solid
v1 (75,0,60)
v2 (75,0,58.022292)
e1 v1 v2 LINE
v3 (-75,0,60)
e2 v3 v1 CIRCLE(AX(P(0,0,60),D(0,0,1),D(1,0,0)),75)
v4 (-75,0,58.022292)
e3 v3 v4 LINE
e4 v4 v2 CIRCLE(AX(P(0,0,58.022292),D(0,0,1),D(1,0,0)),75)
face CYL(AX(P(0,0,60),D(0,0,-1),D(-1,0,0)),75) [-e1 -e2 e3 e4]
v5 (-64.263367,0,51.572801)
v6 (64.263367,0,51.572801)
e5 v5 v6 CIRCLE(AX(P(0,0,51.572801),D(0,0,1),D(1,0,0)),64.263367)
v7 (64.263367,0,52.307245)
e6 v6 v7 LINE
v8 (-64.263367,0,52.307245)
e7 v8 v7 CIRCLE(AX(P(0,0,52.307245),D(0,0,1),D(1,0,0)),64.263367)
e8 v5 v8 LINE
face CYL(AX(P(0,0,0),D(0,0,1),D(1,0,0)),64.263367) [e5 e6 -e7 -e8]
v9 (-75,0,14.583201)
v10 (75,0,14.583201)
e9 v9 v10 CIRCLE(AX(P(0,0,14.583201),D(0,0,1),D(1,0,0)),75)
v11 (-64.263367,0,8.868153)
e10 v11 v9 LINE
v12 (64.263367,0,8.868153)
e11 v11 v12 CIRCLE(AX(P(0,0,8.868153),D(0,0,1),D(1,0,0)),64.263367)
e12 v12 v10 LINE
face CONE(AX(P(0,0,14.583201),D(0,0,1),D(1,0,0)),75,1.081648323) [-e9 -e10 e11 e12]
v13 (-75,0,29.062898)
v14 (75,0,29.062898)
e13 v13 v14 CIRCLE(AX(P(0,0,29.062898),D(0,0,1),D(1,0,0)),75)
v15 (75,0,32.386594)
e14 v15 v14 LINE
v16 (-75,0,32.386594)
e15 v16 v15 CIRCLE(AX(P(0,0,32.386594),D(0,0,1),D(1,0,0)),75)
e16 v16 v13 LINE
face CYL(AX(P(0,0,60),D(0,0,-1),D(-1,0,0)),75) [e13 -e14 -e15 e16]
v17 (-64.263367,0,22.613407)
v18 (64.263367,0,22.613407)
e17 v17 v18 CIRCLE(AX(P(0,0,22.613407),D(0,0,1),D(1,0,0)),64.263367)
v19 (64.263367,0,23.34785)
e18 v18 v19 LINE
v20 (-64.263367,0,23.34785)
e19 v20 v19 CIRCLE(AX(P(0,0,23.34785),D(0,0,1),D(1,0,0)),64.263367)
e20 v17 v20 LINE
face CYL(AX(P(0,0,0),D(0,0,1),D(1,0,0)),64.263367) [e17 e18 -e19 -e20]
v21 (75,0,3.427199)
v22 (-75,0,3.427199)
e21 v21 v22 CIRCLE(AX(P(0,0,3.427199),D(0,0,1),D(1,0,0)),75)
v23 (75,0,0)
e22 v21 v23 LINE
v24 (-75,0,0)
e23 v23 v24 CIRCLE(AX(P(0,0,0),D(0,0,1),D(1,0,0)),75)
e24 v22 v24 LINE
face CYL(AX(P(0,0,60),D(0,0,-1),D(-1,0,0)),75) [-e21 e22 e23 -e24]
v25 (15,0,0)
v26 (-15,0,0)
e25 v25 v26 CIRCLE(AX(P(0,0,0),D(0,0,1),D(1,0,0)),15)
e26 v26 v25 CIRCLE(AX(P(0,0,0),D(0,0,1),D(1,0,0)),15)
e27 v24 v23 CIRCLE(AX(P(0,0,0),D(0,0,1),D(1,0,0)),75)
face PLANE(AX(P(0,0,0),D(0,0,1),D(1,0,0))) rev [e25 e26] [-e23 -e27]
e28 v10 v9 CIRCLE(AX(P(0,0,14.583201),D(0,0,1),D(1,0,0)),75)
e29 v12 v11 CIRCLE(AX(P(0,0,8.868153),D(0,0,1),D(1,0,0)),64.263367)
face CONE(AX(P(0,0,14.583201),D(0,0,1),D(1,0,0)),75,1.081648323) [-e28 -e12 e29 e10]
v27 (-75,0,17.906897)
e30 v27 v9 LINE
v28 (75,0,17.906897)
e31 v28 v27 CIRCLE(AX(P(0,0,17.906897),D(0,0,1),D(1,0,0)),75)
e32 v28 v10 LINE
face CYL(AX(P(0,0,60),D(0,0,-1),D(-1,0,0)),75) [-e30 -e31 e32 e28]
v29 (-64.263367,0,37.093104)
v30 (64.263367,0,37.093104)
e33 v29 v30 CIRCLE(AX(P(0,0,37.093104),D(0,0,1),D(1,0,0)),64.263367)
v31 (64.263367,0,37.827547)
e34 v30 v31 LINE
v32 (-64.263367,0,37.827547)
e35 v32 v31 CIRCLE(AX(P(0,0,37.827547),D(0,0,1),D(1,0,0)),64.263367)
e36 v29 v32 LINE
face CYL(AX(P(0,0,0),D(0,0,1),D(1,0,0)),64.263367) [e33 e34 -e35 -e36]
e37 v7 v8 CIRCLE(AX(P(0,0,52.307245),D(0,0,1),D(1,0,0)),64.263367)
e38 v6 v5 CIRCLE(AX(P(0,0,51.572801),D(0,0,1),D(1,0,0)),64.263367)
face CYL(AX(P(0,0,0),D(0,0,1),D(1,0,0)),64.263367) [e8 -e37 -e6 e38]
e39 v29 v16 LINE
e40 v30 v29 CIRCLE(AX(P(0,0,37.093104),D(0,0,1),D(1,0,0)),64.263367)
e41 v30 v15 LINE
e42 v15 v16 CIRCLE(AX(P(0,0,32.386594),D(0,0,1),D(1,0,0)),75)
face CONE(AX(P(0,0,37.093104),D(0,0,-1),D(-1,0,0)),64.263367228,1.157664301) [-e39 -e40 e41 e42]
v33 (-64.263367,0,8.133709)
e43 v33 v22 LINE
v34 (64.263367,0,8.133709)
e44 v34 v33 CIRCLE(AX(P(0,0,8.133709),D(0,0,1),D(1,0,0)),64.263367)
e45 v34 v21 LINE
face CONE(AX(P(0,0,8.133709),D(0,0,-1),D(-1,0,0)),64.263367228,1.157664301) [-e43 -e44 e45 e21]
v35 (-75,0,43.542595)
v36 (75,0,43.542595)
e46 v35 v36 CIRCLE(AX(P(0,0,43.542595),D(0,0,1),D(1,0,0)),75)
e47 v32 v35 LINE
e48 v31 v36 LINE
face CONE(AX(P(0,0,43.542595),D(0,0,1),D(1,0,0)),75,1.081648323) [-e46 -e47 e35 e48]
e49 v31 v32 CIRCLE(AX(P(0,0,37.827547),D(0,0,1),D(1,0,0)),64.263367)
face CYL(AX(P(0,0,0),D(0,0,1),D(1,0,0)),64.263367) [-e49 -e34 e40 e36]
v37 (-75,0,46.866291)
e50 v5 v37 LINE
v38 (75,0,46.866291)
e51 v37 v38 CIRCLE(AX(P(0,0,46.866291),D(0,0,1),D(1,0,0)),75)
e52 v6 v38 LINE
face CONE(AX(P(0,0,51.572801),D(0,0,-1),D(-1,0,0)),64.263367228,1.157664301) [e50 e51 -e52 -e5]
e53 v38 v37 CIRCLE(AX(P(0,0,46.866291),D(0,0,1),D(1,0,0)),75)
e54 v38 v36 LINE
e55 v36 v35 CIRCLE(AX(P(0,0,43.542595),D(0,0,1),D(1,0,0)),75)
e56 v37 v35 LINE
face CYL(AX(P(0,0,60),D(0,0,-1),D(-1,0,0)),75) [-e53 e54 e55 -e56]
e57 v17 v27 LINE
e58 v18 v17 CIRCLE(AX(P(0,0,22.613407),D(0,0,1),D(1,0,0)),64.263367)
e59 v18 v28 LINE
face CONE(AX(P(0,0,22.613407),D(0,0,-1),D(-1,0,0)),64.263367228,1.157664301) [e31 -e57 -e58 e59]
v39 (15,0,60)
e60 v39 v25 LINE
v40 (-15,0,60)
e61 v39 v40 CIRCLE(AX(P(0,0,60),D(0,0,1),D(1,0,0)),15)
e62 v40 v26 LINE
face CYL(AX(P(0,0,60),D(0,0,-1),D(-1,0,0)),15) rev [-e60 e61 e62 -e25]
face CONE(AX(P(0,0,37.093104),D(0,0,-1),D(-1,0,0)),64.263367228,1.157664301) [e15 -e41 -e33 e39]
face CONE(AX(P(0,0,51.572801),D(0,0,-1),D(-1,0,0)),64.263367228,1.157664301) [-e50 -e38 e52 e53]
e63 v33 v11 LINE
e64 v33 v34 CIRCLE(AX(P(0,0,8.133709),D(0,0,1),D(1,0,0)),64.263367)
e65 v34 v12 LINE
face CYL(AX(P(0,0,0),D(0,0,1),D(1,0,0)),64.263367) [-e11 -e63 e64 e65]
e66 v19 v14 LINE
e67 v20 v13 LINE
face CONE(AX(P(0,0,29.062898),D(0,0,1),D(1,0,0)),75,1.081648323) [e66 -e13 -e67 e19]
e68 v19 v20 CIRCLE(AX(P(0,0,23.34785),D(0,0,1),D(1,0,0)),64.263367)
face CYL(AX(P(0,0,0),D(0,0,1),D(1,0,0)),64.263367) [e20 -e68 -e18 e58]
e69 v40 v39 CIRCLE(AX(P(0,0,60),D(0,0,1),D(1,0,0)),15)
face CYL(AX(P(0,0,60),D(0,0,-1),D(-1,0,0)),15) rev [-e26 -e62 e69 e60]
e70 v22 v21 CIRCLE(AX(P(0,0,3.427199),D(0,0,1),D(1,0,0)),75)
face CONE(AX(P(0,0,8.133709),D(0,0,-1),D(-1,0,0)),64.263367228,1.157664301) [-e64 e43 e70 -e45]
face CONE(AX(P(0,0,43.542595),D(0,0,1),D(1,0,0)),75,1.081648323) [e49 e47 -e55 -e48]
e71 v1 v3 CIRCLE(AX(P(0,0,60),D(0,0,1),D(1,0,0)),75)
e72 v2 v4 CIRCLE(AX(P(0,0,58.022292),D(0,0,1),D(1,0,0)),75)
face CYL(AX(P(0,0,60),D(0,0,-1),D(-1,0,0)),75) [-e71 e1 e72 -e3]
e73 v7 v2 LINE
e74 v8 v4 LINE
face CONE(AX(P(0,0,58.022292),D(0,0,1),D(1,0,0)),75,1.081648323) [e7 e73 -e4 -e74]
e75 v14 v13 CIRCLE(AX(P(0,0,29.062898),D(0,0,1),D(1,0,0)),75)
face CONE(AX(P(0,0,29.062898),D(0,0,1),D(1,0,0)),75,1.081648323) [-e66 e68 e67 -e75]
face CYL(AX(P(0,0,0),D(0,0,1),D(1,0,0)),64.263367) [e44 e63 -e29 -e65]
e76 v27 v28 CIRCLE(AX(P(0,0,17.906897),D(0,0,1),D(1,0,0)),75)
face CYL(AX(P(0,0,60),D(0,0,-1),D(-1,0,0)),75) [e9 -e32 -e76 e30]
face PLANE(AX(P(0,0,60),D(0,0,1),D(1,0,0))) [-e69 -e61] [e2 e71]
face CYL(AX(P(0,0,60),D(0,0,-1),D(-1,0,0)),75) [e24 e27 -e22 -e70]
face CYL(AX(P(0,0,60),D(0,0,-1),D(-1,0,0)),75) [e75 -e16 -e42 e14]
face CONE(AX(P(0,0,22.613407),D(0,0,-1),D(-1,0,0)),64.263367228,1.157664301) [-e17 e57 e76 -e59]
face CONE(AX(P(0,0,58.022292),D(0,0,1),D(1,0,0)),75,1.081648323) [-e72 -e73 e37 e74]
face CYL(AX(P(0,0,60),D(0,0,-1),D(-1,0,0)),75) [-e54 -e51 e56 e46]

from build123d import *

# Parameters (mm, degrees)
SKETCH_1_R      = 75
SKETCH_1_R_2    = 15
EXTRUDE_1_DEPTH = 60


with BuildPart() as part:
    # 草图1 → 凸台-拉伸1 (new body)
    with BuildSketch(Plane.XY):
        Circle(SKETCH_1_R)
        Circle(SKETCH_1_R_2, mode=Mode.SUBTRACT)
    extrude(amount=EXTRUDE_1_DEPTH)

    # 草图2 → 切除-旋转2 (revolve, cut)
    with BuildSketch(Plane(origin=(0, 0, 0), x_dir=(1, 0, 0), z_dir=(0, 1, 0)), mode=Mode.PRIVATE) as cut_revolve_2_sk:
        Polygon((-75, -46.866291189), (-75, -58.022292434), (-64.263367228, -52.307244529), (-64.263367228, -51.572801228), align=None)
        Polygon((-75, -32.38659394), (-75, -43.542595186), (-64.263367228, -37.827547281), (-64.263367228, -37.09310398), align=None)
        Polygon((-75, -17.906896692), (-75, -29.062897938), (-64.263367228, -23.347850033), (-64.263367228, -22.613406731), align=None)
        Polygon((-75, -3.427199444), (-75, -14.583200689), (-64.263367228, -8.868152785), (-64.263367228, -8.133709483), align=None)
    revolve(cut_revolve_2_sk.sketch.rotate(Axis((0, 0, 0), (0, 0, -1)), 180), axis=Axis((0, 0, 0), (0, 0, -1)), mode=Mode.SUBTRACT)


solid = part.part
